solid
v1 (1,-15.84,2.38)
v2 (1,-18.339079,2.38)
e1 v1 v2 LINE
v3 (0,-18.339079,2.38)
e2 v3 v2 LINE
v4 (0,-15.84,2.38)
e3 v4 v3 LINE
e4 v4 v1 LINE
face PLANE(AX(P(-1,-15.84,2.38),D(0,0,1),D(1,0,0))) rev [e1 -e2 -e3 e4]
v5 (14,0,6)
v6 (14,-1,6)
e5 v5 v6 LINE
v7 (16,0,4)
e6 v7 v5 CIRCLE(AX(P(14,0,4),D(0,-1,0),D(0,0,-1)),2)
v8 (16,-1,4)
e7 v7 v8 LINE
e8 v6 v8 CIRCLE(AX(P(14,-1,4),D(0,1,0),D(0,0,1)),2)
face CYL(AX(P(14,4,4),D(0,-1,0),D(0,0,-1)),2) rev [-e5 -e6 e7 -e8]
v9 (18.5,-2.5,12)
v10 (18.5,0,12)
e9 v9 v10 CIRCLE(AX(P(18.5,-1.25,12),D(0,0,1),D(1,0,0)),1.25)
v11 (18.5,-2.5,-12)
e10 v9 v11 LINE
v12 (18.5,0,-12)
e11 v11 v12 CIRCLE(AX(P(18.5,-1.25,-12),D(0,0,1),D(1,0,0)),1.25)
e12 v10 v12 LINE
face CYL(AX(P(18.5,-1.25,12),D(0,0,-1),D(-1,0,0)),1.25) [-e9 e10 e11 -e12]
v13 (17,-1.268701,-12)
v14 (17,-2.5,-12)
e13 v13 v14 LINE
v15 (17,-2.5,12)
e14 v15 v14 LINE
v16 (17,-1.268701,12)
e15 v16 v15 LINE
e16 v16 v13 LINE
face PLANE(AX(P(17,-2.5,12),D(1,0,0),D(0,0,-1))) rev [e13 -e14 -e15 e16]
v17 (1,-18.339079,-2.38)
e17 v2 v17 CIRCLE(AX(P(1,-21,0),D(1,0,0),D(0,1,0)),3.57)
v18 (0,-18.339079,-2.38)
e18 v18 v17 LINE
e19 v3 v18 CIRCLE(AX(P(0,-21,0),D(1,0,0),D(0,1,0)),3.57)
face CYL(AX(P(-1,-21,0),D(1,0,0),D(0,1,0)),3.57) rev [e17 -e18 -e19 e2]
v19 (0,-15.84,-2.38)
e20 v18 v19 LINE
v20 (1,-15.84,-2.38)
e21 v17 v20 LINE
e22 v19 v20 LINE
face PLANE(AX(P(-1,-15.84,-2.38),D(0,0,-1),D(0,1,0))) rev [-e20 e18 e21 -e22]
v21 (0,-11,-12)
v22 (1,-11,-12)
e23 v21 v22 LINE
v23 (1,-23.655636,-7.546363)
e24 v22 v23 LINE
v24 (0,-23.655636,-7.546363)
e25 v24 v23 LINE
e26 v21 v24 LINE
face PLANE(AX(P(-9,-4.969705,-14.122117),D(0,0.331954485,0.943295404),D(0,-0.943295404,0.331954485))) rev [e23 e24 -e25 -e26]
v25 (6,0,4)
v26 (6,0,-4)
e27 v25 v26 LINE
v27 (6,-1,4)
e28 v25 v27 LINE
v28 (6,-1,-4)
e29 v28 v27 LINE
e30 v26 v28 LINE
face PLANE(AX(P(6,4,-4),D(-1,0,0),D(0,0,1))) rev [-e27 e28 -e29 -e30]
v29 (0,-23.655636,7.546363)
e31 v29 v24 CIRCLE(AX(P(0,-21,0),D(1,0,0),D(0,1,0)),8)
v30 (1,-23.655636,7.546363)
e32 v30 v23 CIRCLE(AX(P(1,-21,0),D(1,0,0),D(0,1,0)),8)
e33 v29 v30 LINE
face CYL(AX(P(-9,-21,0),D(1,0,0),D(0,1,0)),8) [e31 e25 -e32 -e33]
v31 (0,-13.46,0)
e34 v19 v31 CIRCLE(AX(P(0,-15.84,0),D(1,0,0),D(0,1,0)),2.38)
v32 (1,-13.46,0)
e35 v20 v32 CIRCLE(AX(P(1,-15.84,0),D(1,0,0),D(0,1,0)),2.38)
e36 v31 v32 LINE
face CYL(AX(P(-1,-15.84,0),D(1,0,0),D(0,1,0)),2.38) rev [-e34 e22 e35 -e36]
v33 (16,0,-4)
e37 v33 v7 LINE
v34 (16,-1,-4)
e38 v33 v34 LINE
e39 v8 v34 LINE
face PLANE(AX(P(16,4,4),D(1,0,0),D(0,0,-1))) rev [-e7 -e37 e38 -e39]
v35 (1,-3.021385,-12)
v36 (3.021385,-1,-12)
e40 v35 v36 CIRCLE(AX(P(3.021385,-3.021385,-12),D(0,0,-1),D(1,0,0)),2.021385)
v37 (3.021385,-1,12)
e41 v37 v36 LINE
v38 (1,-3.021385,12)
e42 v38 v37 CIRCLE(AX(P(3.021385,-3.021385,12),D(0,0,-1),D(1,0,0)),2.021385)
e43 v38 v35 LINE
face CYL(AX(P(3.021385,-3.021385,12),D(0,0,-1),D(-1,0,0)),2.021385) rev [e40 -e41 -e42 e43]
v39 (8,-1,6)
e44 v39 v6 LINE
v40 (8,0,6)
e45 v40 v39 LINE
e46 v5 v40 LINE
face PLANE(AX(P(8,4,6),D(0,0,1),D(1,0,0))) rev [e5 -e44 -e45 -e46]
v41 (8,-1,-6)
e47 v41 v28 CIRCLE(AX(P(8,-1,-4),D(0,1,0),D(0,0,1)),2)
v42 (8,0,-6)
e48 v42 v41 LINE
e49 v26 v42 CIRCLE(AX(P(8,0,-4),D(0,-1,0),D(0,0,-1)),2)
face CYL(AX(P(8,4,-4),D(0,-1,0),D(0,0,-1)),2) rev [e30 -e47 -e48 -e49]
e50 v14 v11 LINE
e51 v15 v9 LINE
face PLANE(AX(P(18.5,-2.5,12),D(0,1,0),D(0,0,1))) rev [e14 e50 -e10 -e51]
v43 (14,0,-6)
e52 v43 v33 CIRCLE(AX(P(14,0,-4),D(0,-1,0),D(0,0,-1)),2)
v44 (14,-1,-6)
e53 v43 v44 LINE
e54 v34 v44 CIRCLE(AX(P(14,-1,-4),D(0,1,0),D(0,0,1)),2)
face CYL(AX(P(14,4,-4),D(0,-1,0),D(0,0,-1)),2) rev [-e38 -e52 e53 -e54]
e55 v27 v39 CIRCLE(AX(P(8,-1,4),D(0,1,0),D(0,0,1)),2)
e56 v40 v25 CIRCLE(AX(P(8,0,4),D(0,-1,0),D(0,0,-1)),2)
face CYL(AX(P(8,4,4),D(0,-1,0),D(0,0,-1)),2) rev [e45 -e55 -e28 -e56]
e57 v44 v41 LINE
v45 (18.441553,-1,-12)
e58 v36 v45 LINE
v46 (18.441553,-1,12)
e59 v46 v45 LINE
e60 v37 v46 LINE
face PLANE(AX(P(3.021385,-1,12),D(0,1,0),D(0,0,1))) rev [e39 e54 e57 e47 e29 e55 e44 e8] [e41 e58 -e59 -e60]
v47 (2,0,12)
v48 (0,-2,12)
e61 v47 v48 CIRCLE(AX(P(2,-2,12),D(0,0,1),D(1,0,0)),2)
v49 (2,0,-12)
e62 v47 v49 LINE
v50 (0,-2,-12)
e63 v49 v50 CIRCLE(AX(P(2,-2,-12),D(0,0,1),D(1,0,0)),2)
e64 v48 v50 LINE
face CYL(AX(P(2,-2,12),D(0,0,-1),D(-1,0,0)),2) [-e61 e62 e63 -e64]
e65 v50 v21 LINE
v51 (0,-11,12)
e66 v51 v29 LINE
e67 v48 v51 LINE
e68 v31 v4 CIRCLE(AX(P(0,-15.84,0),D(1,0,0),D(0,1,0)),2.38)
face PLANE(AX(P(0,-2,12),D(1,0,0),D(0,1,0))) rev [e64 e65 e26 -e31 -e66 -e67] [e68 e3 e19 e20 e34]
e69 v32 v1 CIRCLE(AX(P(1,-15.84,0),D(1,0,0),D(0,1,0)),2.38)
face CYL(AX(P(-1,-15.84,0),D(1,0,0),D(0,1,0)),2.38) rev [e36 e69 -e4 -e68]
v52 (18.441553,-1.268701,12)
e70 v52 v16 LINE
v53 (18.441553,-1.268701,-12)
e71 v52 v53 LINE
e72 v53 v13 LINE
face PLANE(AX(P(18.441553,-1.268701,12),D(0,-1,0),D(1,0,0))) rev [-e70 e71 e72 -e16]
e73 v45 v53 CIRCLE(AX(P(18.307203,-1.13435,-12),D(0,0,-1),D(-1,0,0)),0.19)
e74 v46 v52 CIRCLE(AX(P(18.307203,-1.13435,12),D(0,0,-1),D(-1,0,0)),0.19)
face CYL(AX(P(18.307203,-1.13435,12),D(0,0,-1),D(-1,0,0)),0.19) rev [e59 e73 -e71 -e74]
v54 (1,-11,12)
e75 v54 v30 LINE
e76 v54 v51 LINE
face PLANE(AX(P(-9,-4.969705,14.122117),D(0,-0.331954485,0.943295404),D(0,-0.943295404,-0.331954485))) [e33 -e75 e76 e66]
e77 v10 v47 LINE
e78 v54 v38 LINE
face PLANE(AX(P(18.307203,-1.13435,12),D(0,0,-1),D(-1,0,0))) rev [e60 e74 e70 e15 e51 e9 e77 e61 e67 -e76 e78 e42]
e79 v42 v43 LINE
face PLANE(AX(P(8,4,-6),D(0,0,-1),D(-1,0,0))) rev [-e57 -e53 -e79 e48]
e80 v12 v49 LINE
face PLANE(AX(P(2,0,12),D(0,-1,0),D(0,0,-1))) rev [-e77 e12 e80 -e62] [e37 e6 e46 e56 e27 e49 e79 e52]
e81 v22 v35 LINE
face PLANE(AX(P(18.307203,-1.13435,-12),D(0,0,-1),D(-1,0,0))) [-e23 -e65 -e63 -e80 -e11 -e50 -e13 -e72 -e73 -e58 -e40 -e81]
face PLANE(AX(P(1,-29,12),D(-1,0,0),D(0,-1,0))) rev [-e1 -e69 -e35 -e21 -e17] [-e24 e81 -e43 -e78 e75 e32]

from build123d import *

# Parameters (mm, degrees)
BRACKET_BODY_DEPTH           = 12
RECTANGULAR_WINDOW_CUT_DEPTH = 5
KEYHOLE_SLOT_CUT_DEPTH       = 10
EDGE_NOTCH_CUT_DEPTH         = 2


with BuildPart() as part:
    # Bracket Profile Sketch → Bracket Body (new, symmetric)
    with BuildSketch(Plane.XY):
        with BuildLine():
            Line((2, 0), (18.5, 0))
            ThreePointArc((18.5, 0), (19.75, -1.25), (18.5, -2.5))
            Line((18.5, -2.5), (17, -2.5))
            Line((17, -2.5), (17, -1.268700577))
            Line((17, -1.268700577), (18.441553142, -1.268700577))
            ThreePointArc((18.441553142, -1.268700577), (18.497202853, -1.134350288), (18.441553142, -1))
            Line((18.441553142, -1), (3.021384942, -1))
            ThreePointArc((3.021384942, -1), (1.592049942, -1.592049942), (1, -3.021384942))
            Line((1, -3.021384942), (1, -29))
            Line((1, -29), (0, -29))
            Line((0, -29), (0, -2))
            ThreePointArc((0, -2), (0.585786438, -0.585786438), (2, 0))
        make_face()
    extrude(amount=BRACKET_BODY_DEPTH, both=True)

    # Rectangular Window Sketch → Rectangular Window Cut (cut, symmetric)
    with BuildSketch(Plane.XZ.offset(1)):
        with BuildLine():
            Line((8, -6), (14, -6))
            ThreePointArc((14, -6), (15.414213562, -5.414213562), (16, -4))
            Line((16, -4), (16, 4))
            ThreePointArc((16, 4), (15.414213562, 5.414213562), (14, 6))
            Line((14, 6), (8, 6))
            ThreePointArc((8, 6), (6.585786438, 5.414213562), (6, 4))
            Line((6, 4), (6, -4))
            ThreePointArc((6, -4), (6.585786438, -5.414213562), (8, -6))
        make_face()
    extrude(amount=RECTANGULAR_WINDOW_CUT_DEPTH, both=True, mode=Mode.SUBTRACT)

    # Keyhole Slot Sketch → Keyhole Slot Cut (cut)
    with BuildSketch(Plane(origin=(1, 0, 0), x_dir=(0, 0, -1), z_dir=(1, 0, 0))):
        with BuildLine():
            ThreePointArc((7.546363234, -23.655635881), (4.623576141, -27.52859431), (-3.9e-08, -29))
            Line((-3.9e-08, -29), (12, -29))
            Line((12, -29), (12, -11))
            Line((12, -11), (7.546363234, -23.655635881))
        make_face()
        with BuildLine():
            Line((-7.546363234, -23.655635881), (-12, -11))
            Line((-12, -11), (-12, -29))
            Line((-12, -29), (-3.9e-08, -29))
            ThreePointArc((-3.9e-08, -29), (-4.623576172, -27.528594288), (-7.546363234, -23.655635881))
        make_face()
    extrude(amount=-KEYHOLE_SLOT_CUT_DEPTH, mode=Mode.SUBTRACT)

    # Edge Notch Sketch → Edge Notch Cut (cut)
    with BuildSketch(Plane(origin=(1, 0, 0), x_dir=(0, 0, -1), z_dir=(1, 0, 0))):
        with BuildLine():
            Line((-2.38, -15.84), (-2.38, -18.339079107))
            ThreePointArc((-2.38, -18.339079107), (0, -24.57), (2.38, -18.339079107))
            Line((2.38, -18.339079107), (2.38, -15.84))
            ThreePointArc((2.38, -15.84), (0, -13.46), (-2.38, -15.84))
        make_face()
    extrude(amount=-EDGE_NOTCH_CUT_DEPTH, mode=Mode.SUBTRACT)


solid = part.part
